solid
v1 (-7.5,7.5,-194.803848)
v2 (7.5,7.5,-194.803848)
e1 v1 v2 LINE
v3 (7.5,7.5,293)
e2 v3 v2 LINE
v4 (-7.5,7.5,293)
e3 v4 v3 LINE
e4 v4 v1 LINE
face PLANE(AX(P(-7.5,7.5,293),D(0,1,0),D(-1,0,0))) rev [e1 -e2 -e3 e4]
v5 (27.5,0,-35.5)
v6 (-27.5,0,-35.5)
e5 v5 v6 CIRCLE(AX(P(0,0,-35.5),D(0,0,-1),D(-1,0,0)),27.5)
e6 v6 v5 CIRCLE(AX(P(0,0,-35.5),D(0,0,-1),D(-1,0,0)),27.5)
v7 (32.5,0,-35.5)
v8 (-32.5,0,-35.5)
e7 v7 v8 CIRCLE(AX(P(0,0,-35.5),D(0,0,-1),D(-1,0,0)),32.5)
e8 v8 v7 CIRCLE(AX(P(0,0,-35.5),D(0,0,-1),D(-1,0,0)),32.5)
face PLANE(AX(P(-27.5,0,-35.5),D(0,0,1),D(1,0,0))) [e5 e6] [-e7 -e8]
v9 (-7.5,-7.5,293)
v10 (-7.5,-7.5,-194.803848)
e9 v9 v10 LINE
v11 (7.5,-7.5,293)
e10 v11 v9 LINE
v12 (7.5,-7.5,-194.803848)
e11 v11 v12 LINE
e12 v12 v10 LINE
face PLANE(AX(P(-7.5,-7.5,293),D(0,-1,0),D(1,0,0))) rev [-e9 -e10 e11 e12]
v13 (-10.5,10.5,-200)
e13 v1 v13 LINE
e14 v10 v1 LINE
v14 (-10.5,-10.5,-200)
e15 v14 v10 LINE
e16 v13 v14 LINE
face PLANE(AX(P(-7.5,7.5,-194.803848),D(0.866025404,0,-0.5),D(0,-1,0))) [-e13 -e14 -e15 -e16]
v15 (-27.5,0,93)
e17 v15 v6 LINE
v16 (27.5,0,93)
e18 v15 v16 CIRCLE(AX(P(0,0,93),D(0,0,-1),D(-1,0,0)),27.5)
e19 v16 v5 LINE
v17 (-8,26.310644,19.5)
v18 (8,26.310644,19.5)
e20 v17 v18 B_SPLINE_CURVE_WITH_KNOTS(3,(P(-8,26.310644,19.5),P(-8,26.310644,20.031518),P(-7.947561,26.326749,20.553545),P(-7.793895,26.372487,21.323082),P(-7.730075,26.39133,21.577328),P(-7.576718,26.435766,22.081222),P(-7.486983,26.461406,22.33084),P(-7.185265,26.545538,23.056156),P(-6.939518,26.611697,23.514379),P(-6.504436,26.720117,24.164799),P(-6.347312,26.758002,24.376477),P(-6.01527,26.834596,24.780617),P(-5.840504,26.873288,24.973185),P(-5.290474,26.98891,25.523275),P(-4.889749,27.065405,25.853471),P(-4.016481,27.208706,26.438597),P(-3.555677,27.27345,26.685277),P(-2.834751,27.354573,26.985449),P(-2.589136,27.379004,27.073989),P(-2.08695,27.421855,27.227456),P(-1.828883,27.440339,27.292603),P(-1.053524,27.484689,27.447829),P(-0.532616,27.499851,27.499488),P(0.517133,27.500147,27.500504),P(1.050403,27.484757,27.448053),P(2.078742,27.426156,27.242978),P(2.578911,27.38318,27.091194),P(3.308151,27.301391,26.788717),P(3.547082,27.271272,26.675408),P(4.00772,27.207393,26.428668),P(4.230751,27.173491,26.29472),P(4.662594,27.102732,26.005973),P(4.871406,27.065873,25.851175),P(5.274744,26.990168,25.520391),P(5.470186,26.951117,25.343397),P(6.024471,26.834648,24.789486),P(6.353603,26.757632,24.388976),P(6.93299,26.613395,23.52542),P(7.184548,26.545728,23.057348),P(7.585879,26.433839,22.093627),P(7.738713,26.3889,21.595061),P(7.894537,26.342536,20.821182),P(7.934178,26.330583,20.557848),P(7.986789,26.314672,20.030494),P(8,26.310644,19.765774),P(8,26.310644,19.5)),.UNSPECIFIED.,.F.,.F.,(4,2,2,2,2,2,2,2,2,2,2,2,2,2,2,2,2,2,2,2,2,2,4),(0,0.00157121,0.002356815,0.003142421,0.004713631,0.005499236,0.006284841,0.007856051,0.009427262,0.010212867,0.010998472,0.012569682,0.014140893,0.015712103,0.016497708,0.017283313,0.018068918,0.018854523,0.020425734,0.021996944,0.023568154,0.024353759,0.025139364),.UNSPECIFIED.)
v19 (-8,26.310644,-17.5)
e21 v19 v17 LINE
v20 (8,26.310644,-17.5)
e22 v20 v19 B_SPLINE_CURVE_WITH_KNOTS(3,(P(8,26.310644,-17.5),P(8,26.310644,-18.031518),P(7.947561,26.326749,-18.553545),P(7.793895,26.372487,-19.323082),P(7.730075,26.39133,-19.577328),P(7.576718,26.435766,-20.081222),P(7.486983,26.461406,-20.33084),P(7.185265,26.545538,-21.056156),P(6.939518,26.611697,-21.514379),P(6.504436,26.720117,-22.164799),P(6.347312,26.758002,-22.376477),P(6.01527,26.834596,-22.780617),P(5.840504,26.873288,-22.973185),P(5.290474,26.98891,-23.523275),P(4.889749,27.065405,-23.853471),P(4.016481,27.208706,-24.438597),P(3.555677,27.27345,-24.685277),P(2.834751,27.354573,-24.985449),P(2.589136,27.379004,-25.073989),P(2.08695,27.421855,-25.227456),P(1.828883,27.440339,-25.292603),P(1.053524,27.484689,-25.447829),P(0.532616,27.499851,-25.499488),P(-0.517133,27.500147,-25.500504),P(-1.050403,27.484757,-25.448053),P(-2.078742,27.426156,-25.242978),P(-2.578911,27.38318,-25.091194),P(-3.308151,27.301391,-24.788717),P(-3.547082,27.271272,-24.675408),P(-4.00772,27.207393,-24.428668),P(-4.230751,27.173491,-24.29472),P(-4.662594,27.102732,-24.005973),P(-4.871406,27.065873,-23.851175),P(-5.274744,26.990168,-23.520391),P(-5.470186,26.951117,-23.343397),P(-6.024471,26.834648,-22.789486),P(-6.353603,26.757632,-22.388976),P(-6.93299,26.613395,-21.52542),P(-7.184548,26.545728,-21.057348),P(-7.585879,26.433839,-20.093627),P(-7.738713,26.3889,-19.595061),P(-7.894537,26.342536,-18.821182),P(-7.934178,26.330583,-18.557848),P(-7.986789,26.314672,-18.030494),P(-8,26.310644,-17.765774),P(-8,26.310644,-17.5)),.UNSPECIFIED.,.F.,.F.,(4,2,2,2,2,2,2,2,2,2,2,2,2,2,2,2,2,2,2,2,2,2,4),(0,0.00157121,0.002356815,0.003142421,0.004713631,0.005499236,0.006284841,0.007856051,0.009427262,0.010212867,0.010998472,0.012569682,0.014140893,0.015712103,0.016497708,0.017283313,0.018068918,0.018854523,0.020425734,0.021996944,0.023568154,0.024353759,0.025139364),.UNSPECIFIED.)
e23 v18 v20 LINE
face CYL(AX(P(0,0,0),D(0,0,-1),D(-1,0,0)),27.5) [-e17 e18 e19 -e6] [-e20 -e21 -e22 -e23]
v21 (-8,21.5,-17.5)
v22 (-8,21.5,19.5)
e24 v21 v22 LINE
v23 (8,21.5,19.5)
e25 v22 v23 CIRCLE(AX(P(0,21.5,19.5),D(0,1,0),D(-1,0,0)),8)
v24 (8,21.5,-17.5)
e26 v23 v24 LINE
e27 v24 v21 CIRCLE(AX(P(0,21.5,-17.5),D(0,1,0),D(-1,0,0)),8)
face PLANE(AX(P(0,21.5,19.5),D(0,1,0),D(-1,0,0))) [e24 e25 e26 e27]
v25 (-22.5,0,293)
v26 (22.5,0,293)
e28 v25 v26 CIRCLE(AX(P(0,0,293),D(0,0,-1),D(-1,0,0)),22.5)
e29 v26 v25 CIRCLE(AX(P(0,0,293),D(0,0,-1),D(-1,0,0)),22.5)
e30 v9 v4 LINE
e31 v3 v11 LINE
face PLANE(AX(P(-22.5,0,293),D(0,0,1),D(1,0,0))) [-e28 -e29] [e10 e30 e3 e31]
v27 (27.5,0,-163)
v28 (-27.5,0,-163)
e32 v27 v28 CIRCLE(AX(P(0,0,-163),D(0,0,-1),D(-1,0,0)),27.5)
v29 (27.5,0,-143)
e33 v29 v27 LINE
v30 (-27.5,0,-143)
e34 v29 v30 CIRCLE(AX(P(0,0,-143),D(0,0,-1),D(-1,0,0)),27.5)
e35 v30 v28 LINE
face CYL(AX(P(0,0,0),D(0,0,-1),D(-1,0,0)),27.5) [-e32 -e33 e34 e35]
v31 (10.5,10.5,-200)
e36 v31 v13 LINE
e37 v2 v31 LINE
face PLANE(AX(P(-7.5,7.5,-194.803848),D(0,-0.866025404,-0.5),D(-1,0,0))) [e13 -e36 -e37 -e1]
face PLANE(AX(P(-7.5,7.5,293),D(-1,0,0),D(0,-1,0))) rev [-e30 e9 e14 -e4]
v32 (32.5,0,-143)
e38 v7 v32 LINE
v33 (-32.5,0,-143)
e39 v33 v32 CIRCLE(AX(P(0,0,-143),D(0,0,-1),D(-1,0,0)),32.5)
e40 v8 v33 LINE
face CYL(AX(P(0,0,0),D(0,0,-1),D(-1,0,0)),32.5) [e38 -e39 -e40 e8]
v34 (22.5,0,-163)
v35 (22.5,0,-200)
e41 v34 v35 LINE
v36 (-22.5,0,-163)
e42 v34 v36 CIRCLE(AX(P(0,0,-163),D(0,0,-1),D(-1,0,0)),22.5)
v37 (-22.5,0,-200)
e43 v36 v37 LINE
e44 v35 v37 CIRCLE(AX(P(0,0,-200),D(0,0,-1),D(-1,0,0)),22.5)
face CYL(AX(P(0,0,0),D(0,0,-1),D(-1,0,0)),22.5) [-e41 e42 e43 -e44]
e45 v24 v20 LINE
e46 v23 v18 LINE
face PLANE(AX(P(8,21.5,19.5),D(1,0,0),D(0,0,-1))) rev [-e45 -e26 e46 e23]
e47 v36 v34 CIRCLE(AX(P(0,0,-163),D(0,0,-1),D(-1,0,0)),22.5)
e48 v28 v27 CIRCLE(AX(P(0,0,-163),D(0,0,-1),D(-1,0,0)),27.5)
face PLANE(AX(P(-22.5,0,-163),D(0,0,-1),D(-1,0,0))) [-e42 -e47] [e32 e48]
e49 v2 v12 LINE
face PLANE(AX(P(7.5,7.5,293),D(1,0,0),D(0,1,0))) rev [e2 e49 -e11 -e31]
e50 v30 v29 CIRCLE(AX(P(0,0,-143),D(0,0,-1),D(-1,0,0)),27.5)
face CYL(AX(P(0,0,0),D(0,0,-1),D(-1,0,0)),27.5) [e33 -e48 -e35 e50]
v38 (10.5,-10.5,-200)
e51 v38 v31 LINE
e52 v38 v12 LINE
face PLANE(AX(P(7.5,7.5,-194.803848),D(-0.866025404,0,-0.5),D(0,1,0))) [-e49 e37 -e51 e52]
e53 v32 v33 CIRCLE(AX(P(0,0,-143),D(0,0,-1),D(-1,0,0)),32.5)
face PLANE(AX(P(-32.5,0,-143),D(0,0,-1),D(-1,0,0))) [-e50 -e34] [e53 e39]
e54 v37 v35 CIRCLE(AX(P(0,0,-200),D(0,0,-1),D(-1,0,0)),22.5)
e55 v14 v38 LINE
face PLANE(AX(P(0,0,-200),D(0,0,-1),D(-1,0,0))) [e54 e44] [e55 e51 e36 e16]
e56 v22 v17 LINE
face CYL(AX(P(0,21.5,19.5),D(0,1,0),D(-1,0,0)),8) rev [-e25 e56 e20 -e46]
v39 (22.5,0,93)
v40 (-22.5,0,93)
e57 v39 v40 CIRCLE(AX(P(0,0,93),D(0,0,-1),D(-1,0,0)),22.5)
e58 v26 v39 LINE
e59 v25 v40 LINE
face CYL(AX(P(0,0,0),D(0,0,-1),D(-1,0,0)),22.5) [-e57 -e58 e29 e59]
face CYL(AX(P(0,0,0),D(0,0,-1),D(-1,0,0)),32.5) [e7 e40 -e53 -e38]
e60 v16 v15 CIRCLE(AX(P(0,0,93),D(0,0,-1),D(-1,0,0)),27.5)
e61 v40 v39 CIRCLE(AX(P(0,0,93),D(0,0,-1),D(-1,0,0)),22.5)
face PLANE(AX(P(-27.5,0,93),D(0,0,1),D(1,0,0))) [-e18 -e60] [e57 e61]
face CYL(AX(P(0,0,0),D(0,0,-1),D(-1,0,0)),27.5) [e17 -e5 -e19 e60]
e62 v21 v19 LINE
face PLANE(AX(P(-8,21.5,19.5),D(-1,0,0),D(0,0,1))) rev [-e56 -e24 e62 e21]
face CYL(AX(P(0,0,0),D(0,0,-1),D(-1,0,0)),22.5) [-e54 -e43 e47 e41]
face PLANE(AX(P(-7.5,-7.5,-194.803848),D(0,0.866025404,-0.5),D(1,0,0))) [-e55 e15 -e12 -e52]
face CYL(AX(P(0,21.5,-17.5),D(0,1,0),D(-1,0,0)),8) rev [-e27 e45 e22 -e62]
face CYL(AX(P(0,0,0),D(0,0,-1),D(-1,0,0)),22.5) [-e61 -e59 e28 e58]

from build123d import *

# Parameters (mm, degrees)
SKETCH_2_W          = 15
SKETCH_2_H          = 15
CUT_EXTRUDE_1_DEPTH = 496.137859591
CHAMFER_1_SIZE      = 3
CHAMFER_1_SIZE2     = 5.196152423
CUT_EXTRUDE_2_DEPTH = 6


with BuildPart() as part:
    # 草图1 → 旋转1 (revolve)
    with BuildSketch(Plane(origin=(0, 0, 0), x_dir=(1, 0, 0), z_dir=(0, 1, 0))):
        Polygon((0, 200), (-22.5, 200), (-22.5, 163), (-27.5, 163), (-27.5, 143), (-32.5, 143), (-32.5, 35.5), (-27.5, 35.5), (-27.5, -93), (-22.5, -93), (-22.5, -293), (0, -293), align=None)
    revolve(axis=Axis((0, 0, 0), (0, 0, 1)))

    # 草图2 → 切除-拉伸1 (cut, through all)
    with BuildSketch(Plane(origin=(0, 0, -200), x_dir=(-1, 0, 0), z_dir=(0, 0, -1))):
        Rectangle(SKETCH_2_W, SKETCH_2_H)
    extrude(amount=-CUT_EXTRUDE_1_DEPTH, mode=Mode.SUBTRACT)

    # 倒角1
    chamfer_1_edges = [part.edges().sort_by_distance(p)[0] for p in [
        (7.5, 0, -200),
        (0, -7.5, -200),
        (-7.5, 0, -200),
        (0, 7.5, -200),
    ]]
    chamfer_1_side = [part.faces().sort_by_distance(p)[0] for p in [
        (21.863603897, 0, -200),
    ]]
    chamfer(chamfer_1_edges, length=CHAMFER_1_SIZE, length2=CHAMFER_1_SIZE2, reference=chamfer_1_side[0])

    # 草图3 → 切除-拉伸2 (cut)
    with BuildSketch(Plane(origin=(0, 27.5, 0), x_dir=(1, 0, 0), z_dir=(0, 1, 0))):
        with BuildLine():
            Line((-8, -19.5), (-8, 17.5))
            ThreePointArc((-8, 17.5), (0, 25.5), (8, 17.5))
            Line((8, 17.5), (8, -19.5))
            ThreePointArc((8, -19.5), (0, -27.5), (-8, -19.5))
        make_face()
    extrude(amount=-CUT_EXTRUDE_2_DEPTH, mode=Mode.SUBTRACT)


solid = part.part
